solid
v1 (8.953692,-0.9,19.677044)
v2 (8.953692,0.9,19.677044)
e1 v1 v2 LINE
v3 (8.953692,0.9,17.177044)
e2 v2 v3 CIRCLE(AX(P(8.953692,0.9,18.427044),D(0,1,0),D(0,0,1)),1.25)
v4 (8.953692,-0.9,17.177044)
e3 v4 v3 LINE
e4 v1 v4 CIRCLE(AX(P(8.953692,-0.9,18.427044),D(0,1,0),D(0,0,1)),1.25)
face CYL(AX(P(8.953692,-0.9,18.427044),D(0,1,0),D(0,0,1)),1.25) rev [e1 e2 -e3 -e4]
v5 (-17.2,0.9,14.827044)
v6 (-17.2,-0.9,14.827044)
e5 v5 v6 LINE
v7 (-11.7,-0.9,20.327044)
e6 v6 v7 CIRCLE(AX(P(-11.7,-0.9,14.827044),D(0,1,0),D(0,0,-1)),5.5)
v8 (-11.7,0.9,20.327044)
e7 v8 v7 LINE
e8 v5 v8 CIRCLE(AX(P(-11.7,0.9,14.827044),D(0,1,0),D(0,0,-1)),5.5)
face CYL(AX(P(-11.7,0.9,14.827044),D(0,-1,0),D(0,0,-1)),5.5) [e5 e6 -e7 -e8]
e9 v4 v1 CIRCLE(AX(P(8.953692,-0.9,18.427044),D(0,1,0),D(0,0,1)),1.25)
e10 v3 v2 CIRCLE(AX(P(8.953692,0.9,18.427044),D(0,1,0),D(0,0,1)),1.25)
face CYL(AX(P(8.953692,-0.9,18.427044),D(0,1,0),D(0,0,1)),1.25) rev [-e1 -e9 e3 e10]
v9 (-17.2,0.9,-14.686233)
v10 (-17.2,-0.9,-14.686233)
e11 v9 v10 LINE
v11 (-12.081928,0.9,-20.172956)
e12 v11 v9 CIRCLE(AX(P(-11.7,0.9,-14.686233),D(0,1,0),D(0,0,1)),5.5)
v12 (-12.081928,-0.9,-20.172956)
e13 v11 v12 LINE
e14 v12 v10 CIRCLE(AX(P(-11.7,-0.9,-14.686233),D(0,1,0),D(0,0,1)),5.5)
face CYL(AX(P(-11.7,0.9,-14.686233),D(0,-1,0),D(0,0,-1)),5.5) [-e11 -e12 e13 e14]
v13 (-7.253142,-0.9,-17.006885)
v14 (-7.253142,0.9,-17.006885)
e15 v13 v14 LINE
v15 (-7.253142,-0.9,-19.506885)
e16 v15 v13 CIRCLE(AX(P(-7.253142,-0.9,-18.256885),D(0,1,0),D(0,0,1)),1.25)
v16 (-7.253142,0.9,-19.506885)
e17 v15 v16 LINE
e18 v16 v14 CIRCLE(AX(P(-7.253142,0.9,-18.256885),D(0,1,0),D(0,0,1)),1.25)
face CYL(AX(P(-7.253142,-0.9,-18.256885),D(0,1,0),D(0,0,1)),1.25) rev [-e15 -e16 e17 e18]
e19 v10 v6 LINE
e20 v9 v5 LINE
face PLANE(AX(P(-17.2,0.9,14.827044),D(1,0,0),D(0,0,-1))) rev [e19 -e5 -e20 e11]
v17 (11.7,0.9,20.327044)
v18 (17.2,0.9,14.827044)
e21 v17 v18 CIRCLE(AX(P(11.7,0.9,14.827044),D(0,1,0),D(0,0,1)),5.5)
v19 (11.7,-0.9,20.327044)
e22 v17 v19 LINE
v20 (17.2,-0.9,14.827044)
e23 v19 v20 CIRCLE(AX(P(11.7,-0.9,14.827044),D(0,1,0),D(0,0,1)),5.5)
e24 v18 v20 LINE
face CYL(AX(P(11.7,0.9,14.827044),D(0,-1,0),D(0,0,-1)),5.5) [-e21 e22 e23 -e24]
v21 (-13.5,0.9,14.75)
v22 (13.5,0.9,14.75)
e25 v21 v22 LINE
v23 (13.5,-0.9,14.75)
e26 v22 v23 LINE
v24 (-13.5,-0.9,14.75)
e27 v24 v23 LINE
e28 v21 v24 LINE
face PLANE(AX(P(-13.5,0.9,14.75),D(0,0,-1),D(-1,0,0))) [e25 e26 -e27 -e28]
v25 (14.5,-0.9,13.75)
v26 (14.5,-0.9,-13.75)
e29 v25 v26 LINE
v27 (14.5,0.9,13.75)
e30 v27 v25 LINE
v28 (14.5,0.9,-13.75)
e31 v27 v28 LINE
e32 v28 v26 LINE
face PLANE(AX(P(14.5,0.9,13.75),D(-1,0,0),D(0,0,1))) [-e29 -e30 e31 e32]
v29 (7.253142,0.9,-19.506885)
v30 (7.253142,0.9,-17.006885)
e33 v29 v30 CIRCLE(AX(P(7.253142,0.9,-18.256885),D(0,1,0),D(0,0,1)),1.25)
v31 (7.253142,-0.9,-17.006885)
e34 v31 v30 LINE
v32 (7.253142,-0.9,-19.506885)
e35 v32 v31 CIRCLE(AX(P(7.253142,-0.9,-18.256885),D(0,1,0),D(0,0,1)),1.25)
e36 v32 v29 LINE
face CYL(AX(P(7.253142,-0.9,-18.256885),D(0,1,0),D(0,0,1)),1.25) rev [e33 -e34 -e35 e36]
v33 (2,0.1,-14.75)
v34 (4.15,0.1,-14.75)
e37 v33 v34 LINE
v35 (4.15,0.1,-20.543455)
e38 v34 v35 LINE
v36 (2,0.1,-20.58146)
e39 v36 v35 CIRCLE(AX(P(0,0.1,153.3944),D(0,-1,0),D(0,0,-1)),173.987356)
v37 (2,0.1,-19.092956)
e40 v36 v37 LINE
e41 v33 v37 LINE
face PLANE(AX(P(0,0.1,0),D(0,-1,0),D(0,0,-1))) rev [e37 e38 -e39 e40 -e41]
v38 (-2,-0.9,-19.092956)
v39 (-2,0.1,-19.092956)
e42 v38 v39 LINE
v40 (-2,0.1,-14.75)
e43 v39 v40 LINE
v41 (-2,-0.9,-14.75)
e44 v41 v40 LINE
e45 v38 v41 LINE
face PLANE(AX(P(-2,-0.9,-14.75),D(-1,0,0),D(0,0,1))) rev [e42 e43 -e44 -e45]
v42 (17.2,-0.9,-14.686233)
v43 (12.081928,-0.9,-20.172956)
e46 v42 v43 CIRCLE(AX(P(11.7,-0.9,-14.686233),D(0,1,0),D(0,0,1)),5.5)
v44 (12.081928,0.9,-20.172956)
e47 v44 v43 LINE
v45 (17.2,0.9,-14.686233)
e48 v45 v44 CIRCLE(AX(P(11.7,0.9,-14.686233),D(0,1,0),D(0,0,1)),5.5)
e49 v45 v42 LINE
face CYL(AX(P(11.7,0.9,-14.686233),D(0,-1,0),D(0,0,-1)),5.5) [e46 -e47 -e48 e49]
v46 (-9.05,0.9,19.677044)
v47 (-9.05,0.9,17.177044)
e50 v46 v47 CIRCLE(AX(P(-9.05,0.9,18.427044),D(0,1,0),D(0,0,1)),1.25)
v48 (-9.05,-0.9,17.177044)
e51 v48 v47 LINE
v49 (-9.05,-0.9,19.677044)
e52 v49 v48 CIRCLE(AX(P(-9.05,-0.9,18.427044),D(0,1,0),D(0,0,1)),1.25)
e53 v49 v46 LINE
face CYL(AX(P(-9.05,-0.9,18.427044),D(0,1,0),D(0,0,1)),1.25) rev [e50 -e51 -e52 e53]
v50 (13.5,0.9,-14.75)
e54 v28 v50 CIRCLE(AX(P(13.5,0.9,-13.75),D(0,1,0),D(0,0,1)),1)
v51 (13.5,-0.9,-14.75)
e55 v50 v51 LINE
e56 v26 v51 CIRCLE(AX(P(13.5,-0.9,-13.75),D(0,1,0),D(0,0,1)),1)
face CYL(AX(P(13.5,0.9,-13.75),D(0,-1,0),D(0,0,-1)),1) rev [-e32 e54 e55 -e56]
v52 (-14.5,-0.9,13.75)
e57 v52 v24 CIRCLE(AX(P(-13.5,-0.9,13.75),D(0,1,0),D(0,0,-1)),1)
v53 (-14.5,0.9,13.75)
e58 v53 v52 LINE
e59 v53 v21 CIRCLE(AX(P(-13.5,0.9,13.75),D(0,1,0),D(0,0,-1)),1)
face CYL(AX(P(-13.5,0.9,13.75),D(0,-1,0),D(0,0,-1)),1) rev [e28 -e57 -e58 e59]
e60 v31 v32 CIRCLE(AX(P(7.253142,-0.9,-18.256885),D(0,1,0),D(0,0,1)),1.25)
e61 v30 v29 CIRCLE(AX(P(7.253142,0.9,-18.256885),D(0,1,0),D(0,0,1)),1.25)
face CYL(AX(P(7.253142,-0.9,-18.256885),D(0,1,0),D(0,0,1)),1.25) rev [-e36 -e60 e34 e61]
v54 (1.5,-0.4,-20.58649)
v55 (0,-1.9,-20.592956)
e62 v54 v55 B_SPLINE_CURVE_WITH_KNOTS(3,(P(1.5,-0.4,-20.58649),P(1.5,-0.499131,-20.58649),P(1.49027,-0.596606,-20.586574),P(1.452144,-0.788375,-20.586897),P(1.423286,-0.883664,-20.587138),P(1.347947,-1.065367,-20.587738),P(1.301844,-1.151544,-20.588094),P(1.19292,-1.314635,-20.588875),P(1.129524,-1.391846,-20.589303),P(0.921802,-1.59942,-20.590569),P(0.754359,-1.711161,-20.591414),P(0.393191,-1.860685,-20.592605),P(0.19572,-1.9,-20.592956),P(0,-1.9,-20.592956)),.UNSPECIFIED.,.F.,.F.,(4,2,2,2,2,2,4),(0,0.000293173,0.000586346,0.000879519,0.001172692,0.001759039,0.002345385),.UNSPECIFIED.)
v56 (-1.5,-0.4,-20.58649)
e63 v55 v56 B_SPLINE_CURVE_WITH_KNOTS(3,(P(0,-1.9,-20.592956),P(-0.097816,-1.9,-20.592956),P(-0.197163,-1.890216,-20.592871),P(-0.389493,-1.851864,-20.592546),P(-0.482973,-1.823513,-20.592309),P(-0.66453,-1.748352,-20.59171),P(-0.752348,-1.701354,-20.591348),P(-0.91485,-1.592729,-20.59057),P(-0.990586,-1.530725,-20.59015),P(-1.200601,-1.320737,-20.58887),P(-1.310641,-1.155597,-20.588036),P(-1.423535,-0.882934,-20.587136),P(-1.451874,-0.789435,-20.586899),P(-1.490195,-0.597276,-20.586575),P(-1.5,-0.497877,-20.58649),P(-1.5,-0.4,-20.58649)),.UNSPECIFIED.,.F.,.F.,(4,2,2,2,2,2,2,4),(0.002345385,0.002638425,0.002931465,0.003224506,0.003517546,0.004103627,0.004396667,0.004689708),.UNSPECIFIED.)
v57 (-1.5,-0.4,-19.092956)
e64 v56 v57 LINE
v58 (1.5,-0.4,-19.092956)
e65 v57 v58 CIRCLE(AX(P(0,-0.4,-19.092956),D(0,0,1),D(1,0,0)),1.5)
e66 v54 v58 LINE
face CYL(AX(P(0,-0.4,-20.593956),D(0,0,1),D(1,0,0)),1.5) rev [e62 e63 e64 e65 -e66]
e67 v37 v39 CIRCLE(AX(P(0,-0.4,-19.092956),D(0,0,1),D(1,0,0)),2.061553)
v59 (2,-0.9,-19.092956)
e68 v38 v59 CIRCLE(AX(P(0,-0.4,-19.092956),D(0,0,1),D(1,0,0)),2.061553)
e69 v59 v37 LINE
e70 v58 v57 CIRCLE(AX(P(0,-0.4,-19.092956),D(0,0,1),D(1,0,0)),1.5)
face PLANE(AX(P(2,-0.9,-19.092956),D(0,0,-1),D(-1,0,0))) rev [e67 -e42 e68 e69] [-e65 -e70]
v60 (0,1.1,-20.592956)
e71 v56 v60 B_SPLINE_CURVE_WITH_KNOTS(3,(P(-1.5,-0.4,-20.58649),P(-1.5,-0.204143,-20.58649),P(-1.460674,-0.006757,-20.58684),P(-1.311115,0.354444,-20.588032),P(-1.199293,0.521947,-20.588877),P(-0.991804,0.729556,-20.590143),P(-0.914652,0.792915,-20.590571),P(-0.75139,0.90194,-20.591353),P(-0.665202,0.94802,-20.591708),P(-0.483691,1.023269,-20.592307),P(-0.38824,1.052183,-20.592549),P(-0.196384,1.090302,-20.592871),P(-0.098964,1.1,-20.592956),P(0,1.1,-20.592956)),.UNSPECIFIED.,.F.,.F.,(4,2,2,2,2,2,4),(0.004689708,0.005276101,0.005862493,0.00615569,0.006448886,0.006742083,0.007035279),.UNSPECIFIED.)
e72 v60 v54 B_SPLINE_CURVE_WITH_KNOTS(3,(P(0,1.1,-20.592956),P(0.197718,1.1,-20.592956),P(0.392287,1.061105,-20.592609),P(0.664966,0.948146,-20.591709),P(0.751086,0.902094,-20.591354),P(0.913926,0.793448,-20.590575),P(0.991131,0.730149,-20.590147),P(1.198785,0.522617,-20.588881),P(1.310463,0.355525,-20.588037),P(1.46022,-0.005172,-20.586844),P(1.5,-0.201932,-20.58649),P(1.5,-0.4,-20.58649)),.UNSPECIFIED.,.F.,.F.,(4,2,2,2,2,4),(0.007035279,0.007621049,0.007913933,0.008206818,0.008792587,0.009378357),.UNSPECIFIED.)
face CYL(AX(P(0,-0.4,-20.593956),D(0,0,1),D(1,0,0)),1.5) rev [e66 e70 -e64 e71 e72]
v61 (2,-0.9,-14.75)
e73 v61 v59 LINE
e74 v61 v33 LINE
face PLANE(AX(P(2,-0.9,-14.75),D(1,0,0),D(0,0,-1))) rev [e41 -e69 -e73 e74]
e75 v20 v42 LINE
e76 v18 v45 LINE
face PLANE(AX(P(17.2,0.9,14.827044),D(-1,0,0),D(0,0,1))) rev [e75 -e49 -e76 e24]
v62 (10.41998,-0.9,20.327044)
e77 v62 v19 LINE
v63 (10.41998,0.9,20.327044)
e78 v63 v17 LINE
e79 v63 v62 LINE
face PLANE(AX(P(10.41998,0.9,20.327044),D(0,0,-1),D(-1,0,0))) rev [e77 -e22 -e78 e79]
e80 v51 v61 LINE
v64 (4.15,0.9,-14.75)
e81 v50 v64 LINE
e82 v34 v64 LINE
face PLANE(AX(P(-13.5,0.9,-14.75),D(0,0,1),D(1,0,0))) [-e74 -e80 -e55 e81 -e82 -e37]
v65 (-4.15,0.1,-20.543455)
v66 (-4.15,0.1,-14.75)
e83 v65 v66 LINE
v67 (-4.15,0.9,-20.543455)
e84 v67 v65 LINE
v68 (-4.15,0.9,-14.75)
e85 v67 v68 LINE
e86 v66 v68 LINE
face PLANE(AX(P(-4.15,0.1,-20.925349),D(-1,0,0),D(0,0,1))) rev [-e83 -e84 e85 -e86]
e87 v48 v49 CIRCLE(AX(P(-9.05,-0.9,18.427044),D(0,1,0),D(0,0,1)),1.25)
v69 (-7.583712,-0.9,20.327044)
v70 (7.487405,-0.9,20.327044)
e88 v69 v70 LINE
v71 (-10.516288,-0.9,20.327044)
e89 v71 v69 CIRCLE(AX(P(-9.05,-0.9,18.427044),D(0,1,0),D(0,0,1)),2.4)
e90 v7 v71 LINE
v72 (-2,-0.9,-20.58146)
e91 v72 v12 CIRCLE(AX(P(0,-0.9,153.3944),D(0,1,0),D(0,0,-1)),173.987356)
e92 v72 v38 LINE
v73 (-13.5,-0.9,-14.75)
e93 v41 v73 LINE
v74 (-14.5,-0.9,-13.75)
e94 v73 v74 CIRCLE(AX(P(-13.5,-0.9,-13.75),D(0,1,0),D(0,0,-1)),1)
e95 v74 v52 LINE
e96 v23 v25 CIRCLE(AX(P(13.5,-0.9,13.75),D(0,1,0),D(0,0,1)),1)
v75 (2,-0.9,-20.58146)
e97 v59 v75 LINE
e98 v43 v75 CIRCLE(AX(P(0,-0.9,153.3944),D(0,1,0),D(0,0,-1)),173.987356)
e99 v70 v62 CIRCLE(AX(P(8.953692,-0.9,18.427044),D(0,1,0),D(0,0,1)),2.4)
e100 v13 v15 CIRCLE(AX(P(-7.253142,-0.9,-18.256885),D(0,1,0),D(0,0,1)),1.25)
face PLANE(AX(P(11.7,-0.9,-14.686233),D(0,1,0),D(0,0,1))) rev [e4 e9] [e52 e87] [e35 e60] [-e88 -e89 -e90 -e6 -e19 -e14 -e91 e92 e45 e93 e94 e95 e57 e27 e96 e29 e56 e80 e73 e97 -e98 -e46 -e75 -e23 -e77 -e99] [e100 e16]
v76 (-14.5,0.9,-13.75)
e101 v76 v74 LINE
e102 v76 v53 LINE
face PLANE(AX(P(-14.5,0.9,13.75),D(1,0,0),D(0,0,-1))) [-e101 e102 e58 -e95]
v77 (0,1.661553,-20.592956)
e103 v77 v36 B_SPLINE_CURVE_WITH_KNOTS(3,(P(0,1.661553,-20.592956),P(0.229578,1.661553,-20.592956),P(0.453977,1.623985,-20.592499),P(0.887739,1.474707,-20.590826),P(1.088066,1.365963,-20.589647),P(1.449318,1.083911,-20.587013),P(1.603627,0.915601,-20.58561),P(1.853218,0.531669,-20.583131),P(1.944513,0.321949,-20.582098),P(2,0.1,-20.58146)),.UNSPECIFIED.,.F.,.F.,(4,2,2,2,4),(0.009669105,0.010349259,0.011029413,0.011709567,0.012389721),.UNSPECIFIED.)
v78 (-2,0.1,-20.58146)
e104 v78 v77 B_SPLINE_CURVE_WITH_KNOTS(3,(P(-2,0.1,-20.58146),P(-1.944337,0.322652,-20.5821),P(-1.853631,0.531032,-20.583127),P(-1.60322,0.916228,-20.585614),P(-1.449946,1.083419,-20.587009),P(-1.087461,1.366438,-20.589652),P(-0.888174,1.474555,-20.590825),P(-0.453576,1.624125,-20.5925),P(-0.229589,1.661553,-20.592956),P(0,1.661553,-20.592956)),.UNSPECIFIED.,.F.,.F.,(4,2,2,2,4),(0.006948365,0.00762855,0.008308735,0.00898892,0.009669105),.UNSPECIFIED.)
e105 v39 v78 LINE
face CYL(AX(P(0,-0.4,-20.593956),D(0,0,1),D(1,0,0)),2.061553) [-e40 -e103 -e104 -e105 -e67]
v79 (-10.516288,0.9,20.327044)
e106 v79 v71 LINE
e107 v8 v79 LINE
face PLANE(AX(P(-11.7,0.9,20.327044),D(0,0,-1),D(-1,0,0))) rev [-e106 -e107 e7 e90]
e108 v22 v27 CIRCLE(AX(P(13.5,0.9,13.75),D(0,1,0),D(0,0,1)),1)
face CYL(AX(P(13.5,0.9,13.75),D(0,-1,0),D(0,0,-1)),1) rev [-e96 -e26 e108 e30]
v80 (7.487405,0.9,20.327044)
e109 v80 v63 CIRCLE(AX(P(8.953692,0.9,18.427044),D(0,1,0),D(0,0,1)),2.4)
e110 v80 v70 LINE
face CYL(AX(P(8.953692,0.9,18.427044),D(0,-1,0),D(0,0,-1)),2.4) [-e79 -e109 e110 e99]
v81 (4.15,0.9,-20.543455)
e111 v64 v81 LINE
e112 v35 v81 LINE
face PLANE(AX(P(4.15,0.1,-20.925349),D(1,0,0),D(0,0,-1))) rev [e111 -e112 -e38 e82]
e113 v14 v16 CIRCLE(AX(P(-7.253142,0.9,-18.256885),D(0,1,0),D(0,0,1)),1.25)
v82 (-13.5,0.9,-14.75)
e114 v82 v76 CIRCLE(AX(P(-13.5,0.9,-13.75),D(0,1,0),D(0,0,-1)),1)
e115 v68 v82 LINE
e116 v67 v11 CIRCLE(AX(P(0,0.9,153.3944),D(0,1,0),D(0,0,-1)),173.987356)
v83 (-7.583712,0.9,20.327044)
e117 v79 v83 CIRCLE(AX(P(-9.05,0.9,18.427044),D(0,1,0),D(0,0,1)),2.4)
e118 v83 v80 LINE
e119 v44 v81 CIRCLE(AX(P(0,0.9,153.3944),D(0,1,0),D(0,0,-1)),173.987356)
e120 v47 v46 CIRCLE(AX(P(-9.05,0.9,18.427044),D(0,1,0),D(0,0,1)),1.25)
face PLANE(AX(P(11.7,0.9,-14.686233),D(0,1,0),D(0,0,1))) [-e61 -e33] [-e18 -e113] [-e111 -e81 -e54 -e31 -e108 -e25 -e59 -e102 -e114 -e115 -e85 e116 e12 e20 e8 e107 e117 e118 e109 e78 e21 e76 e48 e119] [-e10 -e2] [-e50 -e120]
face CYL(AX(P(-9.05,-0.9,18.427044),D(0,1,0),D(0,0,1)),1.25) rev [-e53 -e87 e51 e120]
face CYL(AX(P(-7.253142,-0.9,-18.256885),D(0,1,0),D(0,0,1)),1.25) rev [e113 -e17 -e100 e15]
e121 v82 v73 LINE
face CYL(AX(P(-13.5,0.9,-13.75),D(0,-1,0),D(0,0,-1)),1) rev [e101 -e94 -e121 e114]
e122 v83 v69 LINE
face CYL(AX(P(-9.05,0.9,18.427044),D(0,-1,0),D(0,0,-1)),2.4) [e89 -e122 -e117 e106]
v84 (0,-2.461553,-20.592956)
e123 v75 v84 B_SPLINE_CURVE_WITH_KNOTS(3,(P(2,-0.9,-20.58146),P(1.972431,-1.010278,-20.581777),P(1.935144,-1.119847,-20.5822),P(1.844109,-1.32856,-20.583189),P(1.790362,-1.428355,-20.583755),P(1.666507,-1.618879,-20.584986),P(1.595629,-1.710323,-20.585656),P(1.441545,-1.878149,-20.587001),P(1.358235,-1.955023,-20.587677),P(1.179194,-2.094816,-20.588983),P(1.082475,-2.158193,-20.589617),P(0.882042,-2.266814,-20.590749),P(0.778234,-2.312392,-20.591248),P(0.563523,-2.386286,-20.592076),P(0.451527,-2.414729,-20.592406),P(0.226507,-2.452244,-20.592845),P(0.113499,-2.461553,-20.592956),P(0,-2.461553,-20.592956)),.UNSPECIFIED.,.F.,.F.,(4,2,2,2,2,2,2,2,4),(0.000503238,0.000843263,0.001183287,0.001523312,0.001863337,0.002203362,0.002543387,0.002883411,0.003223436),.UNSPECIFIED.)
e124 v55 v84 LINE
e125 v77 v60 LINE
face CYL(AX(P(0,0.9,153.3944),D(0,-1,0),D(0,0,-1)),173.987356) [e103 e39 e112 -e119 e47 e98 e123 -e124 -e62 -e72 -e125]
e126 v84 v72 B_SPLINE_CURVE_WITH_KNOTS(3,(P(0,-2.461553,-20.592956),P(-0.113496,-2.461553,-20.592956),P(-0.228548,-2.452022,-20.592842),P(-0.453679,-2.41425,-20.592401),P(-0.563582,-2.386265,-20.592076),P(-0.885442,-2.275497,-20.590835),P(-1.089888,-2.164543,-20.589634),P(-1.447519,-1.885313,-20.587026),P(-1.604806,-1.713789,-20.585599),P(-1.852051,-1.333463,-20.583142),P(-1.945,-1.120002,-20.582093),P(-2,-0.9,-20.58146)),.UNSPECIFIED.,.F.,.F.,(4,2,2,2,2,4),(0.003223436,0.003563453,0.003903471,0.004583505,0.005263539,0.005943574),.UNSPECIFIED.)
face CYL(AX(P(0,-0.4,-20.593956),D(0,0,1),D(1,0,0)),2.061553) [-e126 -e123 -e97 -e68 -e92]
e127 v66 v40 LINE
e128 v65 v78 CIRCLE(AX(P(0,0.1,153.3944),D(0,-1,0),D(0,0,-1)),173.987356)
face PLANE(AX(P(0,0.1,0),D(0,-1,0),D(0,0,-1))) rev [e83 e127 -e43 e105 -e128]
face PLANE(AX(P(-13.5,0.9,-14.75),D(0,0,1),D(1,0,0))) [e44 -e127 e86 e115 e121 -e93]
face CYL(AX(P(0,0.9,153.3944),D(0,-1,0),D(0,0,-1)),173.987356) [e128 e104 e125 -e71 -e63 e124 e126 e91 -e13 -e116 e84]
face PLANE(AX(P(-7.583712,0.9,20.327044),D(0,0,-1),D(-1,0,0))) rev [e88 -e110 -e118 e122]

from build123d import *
from build123d.topology import SkipClean

# Parameters (mm, degrees)
BOSS_EXTRUDE_1_DEPTH      = 0.9
CUT_EXTRUDE_1_DEPTH       = 28.026205
CUT_EXTRUDE_1_DEPTH_BACK  = 28.026205
SKETCH_2_R                = 1.25
SKETCH_3_W                = 4
SKETCH_3_H                = 4.342956
CUT_EXTRUDE_2_DEPTH       = 1.8
SKETCH_4_W                = 8.3
SKETCH_4_H                = 6.175349
CUT_EXTRUDE3_DEPTH        = 0.8
BOSS_EXTRUDE_2_REACH      = 45.477
BOSS_EXTRUDE_2_END_RADIUS = 173.987356
SKETCH_10_R               = 2.061553
SKETCH_10_R_2             = 1.5
SKETCH_11_R               = 1.5
CUT_EXTRUDE_7_DEPTH       = 10


with BuildPart() as part:
    # Sketch 1 → Boss-Extrude 1 (new, symmetric)
    with BuildSketch(Plane(origin=(0, 0, 0), x_dir=(1, 0, 0), z_dir=(0, 1, 0))):
        with BuildLine():
            Line((-17.2, -14.827044), (-17.2, 14.686233))
            ThreePointArc((-17.2, 14.686233), (-15.721853, 18.437859), (-12.081928, 20.172956))
            ThreePointArc((-12.081928, 20.172956), (0, 20.592956), (12.081928, 20.172956))
            ThreePointArc((12.081928, 20.172956), (15.721853, 18.437859), (17.2, 14.686233))
            Line((17.2, 14.686233), (17.2, -14.827044))
            ThreePointArc((17.2, -14.827044), (15.589087, -18.716131), (11.7, -20.327044))
            Line((11.7, -20.327044), (10.41998, -20.327044))
            ThreePointArc((10.41998, -20.327044), (8.953692, -20.827044), (7.487405, -20.327044))
            Line((7.487405, -20.327044), (-7.583712, -20.327044))
            ThreePointArc((-7.583712, -20.327044), (-9.05, -20.827044), (-10.516288, -20.327044))
            Line((-10.516288, -20.327044), (-11.7, -20.327044))
            ThreePointArc((-11.7, -20.327044), (-15.589087, -18.716131), (-17.2, -14.827044))
        make_face()
        with BuildLine():
            Line((-13.5, -14.75), (13.5, -14.75))
            ThreePointArc((13.5, -14.75), (14.207107, -14.457107), (14.5, -13.75))
            Line((14.5, -13.75), (14.5, 13.75))
            ThreePointArc((14.5, 13.75), (14.207107, 14.457107), (13.5, 14.75))
            Line((13.5, 14.75), (-13.5, 14.75))
            ThreePointArc((-13.5, 14.75), (-14.207107, 14.457107), (-14.5, 13.75))
            Line((-14.5, 13.75), (-14.5, -13.75))
            ThreePointArc((-14.5, -13.75), (-14.207107, -14.457107), (-13.5, -14.75))
        make_face(mode=Mode.SUBTRACT)
    extrude(amount=BOSS_EXTRUDE_1_DEPTH, both=True)

    # Sketch 2 → Cut-Extrude 1 (cut, two sides: drawn at the far end of the back side and taken through both)
    with BuildSketch(Plane(origin=(0, 0, 0), x_dir=(1, 0, 0), z_dir=(0, 1, 0)).offset(-CUT_EXTRUDE_1_DEPTH_BACK)):
        with Locations(Location((-9.05, -18.427044, 0), (0, 0, 270))):
            Circle(SKETCH_2_R)
        with Locations(Location((8.953692, -18.427044, 0), (0, 0, 270))):
            Circle(SKETCH_2_R)
        with Locations(Location((-7.253142, 18.256885, 0), (0, 0, 270))):
            Circle(SKETCH_2_R)
        with Locations(Location((7.253142, 18.256885, 0), (0, 0, 270))):
            Circle(SKETCH_2_R)
    extrude(amount=CUT_EXTRUDE_1_DEPTH + CUT_EXTRUDE_1_DEPTH_BACK, mode=Mode.SUBTRACT)

    # Sketch 3 → Cut-Extrude 2 (cut)
    with BuildSketch(Plane(origin=(0, 0.9, 0), x_dir=(1, 0, 0), z_dir=(0, 1, 0))):
        with Locations((0, 16.921478)):
            Rectangle(SKETCH_3_W, SKETCH_3_H)
    extrude(amount=-CUT_EXTRUDE_2_DEPTH, mode=Mode.SUBTRACT)

    # Sketch 4 → Cut-Extrude3 (cut)
    with BuildSketch(Plane(origin=(0, 0.9, 0), x_dir=(1, 0, 0), z_dir=(0, 1, 0))):
        with Locations((0, 17.837674)):
            Rectangle(SKETCH_4_W, SKETCH_4_H)
    extrude(amount=-CUT_EXTRUDE3_DEPTH, mode=Mode.SUBTRACT)

    # Boss-Extrude 2: up to this cylinder (the profile starts inside it)
    boss_extrude_2_end = Plane(origin=(0, -0.4, 153.3944), z_dir=(0, -1, 0)) * Cylinder(BOSS_EXTRUDE_2_END_RADIUS, 439.928711, mode=Mode.PRIVATE)
    # Sketch 10 → Boss-Extrude 2 (add, up to the surface)
    with BuildSketch(Plane.XY.offset(-19.092956), mode=Mode.PRIVATE) as boss_extrude_2_sk1:
        with Locations((0, -0.4)):
            Circle(SKETCH_10_R)
        with Locations((0, -0.4)):
            Circle(SKETCH_10_R_2, mode=Mode.SUBTRACT)
    boss_extrude_2_tool1 = extrude(boss_extrude_2_sk1.sketch, amount=-BOSS_EXTRUDE_2_REACH, mode=Mode.PRIVATE) & boss_extrude_2_end
    add(boss_extrude_2_tool1.solids().sort_by_distance((-2.003243, -0.4, -19.092956))[0])

    # Sketch 11 → Cut-Extrude 7 (cut)
    with SkipClean():  # the faces are left unmerged after this step: merging them gives an invalid solid
        with BuildSketch(Plane.XY.offset(-19.092956)):
            with Locations((0, -0.4)):
                Circle(SKETCH_11_R)
        extrude(amount=-CUT_EXTRUDE_7_DEPTH, mode=Mode.SUBTRACT)


solid = part.part
